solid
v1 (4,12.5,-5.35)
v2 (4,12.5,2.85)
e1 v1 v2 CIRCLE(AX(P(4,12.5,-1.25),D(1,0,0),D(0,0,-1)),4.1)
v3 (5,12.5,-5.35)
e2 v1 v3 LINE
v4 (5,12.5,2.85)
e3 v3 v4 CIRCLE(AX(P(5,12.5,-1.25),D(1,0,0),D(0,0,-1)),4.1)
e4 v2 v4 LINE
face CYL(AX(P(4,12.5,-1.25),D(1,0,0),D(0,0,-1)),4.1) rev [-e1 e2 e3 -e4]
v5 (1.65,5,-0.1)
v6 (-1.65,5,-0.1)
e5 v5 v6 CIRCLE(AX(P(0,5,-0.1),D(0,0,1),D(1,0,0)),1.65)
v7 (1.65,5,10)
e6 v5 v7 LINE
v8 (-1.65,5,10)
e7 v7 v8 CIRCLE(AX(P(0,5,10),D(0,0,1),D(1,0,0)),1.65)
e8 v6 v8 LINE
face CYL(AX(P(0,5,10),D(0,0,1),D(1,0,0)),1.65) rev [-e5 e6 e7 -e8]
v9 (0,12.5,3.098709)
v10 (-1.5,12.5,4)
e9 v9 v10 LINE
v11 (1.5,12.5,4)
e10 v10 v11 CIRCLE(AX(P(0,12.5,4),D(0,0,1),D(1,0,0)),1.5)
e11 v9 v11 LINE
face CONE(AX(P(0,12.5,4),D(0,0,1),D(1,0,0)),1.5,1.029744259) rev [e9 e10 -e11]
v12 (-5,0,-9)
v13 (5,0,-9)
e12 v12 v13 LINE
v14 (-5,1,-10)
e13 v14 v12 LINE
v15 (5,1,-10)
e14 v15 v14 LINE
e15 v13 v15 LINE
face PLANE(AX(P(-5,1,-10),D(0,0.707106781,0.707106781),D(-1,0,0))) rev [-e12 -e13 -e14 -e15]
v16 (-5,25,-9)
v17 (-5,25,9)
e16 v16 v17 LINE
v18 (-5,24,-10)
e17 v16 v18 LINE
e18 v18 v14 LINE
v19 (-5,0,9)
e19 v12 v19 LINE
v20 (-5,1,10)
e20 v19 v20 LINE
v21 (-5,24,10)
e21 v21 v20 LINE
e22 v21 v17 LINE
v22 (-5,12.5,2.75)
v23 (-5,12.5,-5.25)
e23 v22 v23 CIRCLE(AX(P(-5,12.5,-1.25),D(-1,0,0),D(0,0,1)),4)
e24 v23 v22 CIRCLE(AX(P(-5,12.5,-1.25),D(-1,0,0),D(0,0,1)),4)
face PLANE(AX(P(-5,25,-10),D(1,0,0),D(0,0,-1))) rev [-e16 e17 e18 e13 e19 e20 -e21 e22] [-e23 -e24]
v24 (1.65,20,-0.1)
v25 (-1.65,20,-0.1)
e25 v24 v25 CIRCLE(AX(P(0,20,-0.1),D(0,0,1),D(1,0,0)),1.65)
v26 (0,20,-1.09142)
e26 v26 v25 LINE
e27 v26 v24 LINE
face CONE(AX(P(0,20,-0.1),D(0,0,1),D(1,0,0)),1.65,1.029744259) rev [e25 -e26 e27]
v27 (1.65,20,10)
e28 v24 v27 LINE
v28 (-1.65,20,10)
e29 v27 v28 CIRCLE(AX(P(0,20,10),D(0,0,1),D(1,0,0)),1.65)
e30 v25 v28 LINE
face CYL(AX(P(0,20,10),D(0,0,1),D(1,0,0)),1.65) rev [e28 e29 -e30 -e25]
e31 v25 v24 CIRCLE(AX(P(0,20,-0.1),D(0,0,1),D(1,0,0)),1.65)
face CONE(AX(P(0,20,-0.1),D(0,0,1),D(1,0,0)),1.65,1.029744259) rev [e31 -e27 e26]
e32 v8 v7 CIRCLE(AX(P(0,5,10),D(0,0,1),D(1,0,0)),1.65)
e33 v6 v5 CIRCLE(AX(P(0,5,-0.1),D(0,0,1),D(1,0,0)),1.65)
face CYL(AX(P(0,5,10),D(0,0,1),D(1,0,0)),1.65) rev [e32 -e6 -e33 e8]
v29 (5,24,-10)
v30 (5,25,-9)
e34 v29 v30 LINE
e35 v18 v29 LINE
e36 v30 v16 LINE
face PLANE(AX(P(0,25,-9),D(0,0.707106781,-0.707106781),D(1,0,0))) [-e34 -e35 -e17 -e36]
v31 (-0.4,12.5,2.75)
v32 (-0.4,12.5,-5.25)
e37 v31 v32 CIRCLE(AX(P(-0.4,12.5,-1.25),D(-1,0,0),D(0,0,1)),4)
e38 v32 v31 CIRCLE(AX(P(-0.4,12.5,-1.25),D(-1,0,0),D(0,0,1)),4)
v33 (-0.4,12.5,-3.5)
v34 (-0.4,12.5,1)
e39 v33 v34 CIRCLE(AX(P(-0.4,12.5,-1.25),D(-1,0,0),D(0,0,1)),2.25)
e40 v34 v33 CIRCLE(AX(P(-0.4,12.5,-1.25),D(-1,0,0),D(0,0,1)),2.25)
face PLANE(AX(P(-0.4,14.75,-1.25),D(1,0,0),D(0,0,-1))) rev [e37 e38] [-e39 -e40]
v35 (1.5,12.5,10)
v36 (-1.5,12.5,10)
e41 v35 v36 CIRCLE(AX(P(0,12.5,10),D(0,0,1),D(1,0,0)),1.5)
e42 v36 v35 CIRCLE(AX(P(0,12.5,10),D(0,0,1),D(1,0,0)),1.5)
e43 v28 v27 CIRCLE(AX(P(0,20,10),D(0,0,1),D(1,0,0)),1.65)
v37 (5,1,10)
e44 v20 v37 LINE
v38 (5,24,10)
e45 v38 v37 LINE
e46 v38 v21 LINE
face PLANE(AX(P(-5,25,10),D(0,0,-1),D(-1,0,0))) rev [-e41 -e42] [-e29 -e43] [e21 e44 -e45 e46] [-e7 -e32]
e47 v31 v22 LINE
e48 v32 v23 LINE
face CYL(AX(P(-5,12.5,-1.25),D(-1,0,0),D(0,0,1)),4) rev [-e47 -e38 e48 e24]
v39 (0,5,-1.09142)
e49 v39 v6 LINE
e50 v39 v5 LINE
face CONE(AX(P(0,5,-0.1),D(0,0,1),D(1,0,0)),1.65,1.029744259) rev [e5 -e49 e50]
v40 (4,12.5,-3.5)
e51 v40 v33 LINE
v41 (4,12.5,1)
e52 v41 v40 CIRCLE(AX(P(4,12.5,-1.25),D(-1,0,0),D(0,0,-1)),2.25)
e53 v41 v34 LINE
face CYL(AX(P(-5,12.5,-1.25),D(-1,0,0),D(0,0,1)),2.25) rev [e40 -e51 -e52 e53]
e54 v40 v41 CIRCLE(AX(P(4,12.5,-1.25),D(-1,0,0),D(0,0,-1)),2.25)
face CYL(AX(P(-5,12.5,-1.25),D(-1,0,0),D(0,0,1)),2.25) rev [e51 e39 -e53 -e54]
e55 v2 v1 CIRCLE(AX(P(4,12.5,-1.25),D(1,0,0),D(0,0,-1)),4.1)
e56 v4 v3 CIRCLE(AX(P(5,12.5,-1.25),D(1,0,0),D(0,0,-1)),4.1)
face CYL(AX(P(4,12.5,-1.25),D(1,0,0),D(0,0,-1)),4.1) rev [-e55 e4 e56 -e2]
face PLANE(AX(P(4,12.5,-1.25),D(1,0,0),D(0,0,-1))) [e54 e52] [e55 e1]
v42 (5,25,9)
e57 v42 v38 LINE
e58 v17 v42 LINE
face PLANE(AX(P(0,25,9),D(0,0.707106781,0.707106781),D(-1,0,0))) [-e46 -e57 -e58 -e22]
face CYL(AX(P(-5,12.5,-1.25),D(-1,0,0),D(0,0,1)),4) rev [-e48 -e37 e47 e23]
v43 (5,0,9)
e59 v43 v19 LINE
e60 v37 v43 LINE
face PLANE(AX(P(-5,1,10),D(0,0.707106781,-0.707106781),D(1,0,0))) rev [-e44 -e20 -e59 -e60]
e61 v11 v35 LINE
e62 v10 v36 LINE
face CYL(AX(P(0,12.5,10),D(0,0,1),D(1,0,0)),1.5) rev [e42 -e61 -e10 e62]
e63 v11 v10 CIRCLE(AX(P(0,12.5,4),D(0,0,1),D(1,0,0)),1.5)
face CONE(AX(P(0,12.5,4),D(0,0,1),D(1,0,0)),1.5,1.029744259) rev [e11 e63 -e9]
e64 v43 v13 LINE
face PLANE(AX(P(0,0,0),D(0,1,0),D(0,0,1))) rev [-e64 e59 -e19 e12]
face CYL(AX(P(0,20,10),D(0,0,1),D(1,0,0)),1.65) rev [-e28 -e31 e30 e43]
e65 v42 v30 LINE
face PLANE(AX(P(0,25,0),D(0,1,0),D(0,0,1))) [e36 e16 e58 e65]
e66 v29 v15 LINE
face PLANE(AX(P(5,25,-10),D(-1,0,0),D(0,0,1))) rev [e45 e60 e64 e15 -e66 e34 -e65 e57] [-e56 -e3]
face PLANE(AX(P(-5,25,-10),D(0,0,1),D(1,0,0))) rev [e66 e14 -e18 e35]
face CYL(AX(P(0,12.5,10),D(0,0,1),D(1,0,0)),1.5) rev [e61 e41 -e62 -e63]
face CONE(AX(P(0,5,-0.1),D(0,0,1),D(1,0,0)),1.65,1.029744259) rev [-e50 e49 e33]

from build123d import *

# Parameters (mm, degrees)
SKETCH_1_W                = 10
SKETCH_1_H                = 20
EXTRUDE_1_DEPTH           = 25
HOLE_WIZARD_1_D           = 4.5
HOLE_WIZARD_1_DEPTH       = 10.1
HOLE_WIZARD_1_CBORE_D     = 8
HOLE_WIZARD_1_CBORE_DEPTH = 4.6
HOLE_WIZARD_1_TIP         = 1.351936393
SKETCH_4_R                = 4.1
CUT_EXTRUDE_1_DEPTH       = 1
HOLE_WIZARD_M4_1_D        = 3.3
HOLE_WIZARD_M4_1_DEPTH    = 10.1
HOLE_WIZARD_M4_1_TIP      = 0.991420021
MM_1_D                    = 3
MM_1_DEPTH                = 6
MM_1_TIP                  = 0.901290929
CHAMFER_1_SIZE            = 1


with BuildPart() as part:
    # 草图1 → 凸台-拉伸1 (new body)
    with BuildSketch(Plane(origin=(0, 0, 0), x_dir=(1, 0, 0), z_dir=(0, 1, 0))):
        Rectangle(SKETCH_1_W, SKETCH_1_H)
    extrude(amount=EXTRUDE_1_DEPTH)

    # 打孔尺寸(%根据)内六角圆柱头螺钉的类型1
    with Locations(Plane.ZY.offset(5)):
        with Locations((-1.25, 12.5)):
            CounterBoreHole(HOLE_WIZARD_1_D / 2, HOLE_WIZARD_1_CBORE_D / 2, HOLE_WIZARD_1_CBORE_DEPTH, depth=HOLE_WIZARD_1_DEPTH)
            with Locations((0, 0, -(HOLE_WIZARD_1_DEPTH + HOLE_WIZARD_1_TIP / 2))):  # 118° drill point
                Cone(0, HOLE_WIZARD_1_D / 2, HOLE_WIZARD_1_TIP, mode=Mode.SUBTRACT)

    # 草图4 → 切除-拉伸1 (cut)
    with BuildSketch(Plane(origin=(5, 0, 0), x_dir=(0, 0, -1), z_dir=(1, 0, 0))):
        with Locations((1.25, 12.5)):
            Circle(SKETCH_4_R)
    extrude(amount=-CUT_EXTRUDE_1_DEPTH, mode=Mode.SUBTRACT)

    # M4 螺纹孔1
    with Locations(Plane.XY.offset(10)):
        with Locations((0, 20), (0, 5)):
            Hole(HOLE_WIZARD_M4_1_D / 2, depth=HOLE_WIZARD_M4_1_DEPTH)
            with Locations((0, 0, -(HOLE_WIZARD_M4_1_DEPTH + HOLE_WIZARD_M4_1_TIP / 2))):  # 118° drill point
                Cone(0, HOLE_WIZARD_M4_1_D / 2, HOLE_WIZARD_M4_1_TIP, mode=Mode.SUBTRACT)

    # 大小mm 暗销孔1
    with Locations(Plane.XY.offset(10)):
        with Locations((0, 12.5)):
            Hole(MM_1_D / 2, depth=MM_1_DEPTH)
            with Locations((0, 0, -(MM_1_DEPTH + MM_1_TIP / 2))):  # 118° drill point
                Cone(0, MM_1_D / 2, MM_1_TIP, mode=Mode.SUBTRACT)

    # 倒角1
    chamfer_1_edges = [part.edges().sort_by_distance(p)[0] for p in [
        (0, 25, 10),
        (0, 0, 10),
        (0, 0, -10),
        (0, 25, -10),
    ]]
    chamfer(chamfer_1_edges, length=CHAMFER_1_SIZE)


solid = part.part
